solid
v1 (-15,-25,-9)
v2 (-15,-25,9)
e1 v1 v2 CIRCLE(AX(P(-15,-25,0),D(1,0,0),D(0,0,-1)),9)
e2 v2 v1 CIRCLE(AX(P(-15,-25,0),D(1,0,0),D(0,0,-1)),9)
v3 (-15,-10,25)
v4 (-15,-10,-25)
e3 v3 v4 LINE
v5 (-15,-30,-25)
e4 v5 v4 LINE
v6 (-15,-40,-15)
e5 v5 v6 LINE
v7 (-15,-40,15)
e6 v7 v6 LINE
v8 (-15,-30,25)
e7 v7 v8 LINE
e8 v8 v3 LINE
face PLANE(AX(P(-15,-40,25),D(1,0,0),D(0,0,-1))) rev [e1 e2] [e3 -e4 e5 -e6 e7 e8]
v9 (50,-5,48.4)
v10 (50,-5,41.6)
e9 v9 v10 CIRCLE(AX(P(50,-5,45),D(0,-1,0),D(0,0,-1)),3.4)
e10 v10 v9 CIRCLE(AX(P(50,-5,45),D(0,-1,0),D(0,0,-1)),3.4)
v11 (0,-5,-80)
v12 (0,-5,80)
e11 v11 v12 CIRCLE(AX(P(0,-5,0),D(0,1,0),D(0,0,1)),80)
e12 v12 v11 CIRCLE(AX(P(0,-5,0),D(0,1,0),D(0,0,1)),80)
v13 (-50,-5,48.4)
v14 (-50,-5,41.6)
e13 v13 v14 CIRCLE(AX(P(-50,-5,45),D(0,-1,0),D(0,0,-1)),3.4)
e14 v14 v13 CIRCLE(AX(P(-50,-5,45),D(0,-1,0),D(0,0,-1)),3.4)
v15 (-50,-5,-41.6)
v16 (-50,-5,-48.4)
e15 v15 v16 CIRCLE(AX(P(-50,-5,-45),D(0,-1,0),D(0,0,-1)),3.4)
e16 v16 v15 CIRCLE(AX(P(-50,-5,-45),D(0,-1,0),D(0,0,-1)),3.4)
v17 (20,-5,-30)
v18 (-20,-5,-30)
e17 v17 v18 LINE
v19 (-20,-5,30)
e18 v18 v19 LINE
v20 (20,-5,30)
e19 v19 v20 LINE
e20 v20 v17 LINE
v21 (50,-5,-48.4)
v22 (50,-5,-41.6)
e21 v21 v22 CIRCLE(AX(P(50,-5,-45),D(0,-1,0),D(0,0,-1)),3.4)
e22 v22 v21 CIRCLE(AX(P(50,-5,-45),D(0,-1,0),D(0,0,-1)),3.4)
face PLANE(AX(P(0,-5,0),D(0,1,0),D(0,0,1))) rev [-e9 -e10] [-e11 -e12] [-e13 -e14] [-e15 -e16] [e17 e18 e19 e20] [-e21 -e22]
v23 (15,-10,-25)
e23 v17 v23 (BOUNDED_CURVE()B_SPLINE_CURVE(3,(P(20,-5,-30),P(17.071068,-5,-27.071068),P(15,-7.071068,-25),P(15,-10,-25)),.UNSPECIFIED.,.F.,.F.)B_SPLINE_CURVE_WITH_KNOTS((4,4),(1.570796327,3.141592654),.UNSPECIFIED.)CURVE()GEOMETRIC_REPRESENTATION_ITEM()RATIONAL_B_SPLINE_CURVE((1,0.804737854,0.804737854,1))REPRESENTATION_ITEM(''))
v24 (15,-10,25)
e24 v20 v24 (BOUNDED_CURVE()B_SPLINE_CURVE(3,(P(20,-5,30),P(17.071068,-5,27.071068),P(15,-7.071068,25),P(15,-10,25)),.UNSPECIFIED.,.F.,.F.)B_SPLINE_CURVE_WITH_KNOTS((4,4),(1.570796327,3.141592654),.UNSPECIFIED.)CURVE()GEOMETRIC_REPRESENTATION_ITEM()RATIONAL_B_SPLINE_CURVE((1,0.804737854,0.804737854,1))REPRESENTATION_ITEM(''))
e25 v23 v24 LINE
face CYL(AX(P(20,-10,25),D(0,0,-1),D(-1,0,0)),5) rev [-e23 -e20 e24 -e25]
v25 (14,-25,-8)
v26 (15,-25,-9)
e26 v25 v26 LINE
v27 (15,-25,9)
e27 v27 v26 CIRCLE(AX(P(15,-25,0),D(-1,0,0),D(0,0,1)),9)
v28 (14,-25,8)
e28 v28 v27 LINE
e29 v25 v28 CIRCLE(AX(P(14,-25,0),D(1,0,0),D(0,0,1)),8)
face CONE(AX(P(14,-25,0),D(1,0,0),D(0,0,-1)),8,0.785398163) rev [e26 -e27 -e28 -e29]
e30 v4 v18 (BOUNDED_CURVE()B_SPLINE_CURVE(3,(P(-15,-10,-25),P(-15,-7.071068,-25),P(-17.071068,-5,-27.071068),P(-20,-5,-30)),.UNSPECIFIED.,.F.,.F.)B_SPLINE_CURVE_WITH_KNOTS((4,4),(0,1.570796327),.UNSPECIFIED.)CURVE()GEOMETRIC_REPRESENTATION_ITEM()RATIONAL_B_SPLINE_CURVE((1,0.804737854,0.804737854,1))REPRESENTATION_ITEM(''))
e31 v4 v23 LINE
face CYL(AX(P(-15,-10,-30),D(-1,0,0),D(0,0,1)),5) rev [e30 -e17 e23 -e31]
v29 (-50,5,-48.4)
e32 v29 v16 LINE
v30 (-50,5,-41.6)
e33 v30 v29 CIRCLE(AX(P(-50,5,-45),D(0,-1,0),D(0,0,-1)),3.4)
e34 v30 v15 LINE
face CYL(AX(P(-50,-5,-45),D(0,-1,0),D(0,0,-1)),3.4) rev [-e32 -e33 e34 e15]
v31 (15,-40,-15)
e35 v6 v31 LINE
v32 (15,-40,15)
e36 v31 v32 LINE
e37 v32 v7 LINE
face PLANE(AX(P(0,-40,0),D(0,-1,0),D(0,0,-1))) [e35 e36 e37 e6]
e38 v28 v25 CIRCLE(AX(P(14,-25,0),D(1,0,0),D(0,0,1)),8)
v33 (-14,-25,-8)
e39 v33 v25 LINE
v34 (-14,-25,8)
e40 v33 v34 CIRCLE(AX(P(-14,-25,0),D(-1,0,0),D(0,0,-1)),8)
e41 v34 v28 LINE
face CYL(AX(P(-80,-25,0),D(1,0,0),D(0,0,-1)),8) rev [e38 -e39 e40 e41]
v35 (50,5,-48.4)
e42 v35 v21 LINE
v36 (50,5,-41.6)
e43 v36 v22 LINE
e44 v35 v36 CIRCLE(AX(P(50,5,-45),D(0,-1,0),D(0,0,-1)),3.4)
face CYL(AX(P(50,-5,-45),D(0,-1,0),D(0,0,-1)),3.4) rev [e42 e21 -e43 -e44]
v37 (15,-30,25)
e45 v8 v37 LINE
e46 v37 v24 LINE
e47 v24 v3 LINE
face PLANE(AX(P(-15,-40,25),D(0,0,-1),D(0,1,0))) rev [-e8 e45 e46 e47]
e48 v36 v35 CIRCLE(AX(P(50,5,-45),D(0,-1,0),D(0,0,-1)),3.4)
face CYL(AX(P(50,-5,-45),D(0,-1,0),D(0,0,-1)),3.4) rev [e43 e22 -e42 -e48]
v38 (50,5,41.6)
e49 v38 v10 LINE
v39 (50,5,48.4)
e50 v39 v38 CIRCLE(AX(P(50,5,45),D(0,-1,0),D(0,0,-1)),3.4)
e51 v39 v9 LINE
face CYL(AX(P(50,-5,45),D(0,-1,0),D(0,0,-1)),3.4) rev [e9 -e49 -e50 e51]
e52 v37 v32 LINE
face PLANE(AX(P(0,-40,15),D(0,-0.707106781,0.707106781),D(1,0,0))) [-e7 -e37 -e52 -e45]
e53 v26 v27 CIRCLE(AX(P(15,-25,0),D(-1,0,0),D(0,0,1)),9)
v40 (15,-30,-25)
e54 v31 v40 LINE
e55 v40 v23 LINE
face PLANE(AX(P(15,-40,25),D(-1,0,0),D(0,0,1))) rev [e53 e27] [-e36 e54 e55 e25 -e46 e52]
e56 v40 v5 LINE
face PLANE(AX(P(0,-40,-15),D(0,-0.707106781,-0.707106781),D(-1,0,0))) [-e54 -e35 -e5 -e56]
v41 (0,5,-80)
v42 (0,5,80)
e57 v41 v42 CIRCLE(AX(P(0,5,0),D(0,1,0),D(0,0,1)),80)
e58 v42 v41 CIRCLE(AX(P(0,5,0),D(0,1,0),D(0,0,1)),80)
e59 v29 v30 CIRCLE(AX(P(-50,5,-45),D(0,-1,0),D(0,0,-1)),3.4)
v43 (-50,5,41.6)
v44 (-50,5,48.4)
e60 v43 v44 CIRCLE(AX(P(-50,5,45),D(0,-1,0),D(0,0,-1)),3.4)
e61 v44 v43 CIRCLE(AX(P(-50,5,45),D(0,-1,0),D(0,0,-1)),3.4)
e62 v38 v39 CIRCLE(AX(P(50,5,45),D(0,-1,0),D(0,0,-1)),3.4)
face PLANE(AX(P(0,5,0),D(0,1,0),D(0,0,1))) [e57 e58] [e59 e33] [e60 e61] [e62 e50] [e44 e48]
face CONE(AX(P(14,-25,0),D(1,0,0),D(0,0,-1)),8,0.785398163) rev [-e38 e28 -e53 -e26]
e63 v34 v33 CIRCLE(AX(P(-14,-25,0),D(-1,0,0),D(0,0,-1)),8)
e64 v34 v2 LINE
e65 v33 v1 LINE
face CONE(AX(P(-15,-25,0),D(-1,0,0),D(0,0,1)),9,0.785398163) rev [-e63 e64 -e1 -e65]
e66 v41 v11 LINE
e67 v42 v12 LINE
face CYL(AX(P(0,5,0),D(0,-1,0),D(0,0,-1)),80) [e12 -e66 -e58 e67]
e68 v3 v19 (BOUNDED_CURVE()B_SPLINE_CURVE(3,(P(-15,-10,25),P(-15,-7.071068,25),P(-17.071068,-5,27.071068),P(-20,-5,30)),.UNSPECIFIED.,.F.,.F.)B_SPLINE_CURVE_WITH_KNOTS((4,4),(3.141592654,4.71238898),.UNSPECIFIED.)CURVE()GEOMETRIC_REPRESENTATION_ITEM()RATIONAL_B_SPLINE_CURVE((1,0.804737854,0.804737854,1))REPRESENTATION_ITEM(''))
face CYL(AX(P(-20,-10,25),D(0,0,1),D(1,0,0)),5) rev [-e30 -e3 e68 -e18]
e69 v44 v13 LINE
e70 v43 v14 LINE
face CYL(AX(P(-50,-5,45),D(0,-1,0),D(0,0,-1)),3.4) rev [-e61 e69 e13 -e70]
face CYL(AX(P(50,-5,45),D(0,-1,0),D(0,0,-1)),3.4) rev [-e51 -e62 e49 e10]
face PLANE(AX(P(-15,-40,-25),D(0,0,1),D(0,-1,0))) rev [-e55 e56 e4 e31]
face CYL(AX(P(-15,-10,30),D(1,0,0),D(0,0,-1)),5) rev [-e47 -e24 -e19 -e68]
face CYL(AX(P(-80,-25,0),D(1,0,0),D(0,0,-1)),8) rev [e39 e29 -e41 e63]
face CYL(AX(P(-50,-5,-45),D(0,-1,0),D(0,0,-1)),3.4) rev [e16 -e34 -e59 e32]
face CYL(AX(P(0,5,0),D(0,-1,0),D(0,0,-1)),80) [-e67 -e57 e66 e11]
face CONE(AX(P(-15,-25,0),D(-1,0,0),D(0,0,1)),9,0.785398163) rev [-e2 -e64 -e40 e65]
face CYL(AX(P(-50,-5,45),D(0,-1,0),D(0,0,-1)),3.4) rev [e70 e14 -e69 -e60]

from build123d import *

# Parameters (mm, degrees)
SKETCH1_R           = 80
BOSS_EXTRUDE1_DEPTH = 5
M8_TAPPED_HOLE1_D   = 6.8
SKETCH7_W           = 30
SKETCH7_H           = 50
BOSS_EXTRUDE2_DEPTH = 35
SKETCH8_R           = 8
CUT_EXTRUDE4_DEPTH  = 131.479883507
CHAMFER1_SIZE       = 10
FILLET3_R           = 5
CHAMFER2_SIZE       = 1


with BuildPart() as part:
    # Sketch1 → Boss-Extrude1 (new, symmetric)
    with BuildSketch(Plane(origin=(0, 0, 0), x_dir=(1, 0, 0), z_dir=(0, 1, 0))):
        with Locations(Location((0, 0, 0), (0, 0, 270))):
            Circle(SKETCH1_R)
    extrude(amount=BOSS_EXTRUDE1_DEPTH, both=True)

    # M8 Tapped Hole1 (through all)
    with Locations(Plane(origin=(0, -5, 0), x_dir=(-1, 0, 0), z_dir=(0, -1, 0))):
        with Locations((50, -45), (50, 45), (-50, 45), (-50, -45)):
            Hole(M8_TAPPED_HOLE1_D / 2)

    # Sketch7 → Boss-Extrude2 (add)
    with BuildSketch(Plane.XZ.offset(5)):
        Rectangle(SKETCH7_W, SKETCH7_H)
    extrude(amount=BOSS_EXTRUDE2_DEPTH)

    # Sketch8 → Cut-Extrude4 (cut, through all)
    with BuildSketch(Plane(origin=(15, 0, 0), x_dir=(0, 0, -1), z_dir=(1, 0, 0))):
        with Locations((0, -25)):
            Circle(SKETCH8_R)
    extrude(amount=-CUT_EXTRUDE4_DEPTH, mode=Mode.SUBTRACT)

    # Chamfer1
    chamfer1_edges = [part.edges().sort_by_distance(p)[0] for p in [
        (0, -40, 25),
        (0, -40, -25),
    ]]
    chamfer(chamfer1_edges, length=CHAMFER1_SIZE)

    # Fillet3
    fillet3_edges = [part.edges().sort_by_distance(p)[0] for p in [
        (15, -5, 0),
        (0, -5, 25),
        (-15, -5, 0),
        (0, -5, -25),
    ]]
    fillet(fillet3_edges, radius=FILLET3_R)

    # Chamfer2
    chamfer2_edges = [part.edges().sort_by_distance(p)[0] for p in [
        (-15, -25, 8),
        (15, -25, 8),
    ]]
    chamfer(chamfer2_edges, length=CHAMFER2_SIZE)


solid = part.part
